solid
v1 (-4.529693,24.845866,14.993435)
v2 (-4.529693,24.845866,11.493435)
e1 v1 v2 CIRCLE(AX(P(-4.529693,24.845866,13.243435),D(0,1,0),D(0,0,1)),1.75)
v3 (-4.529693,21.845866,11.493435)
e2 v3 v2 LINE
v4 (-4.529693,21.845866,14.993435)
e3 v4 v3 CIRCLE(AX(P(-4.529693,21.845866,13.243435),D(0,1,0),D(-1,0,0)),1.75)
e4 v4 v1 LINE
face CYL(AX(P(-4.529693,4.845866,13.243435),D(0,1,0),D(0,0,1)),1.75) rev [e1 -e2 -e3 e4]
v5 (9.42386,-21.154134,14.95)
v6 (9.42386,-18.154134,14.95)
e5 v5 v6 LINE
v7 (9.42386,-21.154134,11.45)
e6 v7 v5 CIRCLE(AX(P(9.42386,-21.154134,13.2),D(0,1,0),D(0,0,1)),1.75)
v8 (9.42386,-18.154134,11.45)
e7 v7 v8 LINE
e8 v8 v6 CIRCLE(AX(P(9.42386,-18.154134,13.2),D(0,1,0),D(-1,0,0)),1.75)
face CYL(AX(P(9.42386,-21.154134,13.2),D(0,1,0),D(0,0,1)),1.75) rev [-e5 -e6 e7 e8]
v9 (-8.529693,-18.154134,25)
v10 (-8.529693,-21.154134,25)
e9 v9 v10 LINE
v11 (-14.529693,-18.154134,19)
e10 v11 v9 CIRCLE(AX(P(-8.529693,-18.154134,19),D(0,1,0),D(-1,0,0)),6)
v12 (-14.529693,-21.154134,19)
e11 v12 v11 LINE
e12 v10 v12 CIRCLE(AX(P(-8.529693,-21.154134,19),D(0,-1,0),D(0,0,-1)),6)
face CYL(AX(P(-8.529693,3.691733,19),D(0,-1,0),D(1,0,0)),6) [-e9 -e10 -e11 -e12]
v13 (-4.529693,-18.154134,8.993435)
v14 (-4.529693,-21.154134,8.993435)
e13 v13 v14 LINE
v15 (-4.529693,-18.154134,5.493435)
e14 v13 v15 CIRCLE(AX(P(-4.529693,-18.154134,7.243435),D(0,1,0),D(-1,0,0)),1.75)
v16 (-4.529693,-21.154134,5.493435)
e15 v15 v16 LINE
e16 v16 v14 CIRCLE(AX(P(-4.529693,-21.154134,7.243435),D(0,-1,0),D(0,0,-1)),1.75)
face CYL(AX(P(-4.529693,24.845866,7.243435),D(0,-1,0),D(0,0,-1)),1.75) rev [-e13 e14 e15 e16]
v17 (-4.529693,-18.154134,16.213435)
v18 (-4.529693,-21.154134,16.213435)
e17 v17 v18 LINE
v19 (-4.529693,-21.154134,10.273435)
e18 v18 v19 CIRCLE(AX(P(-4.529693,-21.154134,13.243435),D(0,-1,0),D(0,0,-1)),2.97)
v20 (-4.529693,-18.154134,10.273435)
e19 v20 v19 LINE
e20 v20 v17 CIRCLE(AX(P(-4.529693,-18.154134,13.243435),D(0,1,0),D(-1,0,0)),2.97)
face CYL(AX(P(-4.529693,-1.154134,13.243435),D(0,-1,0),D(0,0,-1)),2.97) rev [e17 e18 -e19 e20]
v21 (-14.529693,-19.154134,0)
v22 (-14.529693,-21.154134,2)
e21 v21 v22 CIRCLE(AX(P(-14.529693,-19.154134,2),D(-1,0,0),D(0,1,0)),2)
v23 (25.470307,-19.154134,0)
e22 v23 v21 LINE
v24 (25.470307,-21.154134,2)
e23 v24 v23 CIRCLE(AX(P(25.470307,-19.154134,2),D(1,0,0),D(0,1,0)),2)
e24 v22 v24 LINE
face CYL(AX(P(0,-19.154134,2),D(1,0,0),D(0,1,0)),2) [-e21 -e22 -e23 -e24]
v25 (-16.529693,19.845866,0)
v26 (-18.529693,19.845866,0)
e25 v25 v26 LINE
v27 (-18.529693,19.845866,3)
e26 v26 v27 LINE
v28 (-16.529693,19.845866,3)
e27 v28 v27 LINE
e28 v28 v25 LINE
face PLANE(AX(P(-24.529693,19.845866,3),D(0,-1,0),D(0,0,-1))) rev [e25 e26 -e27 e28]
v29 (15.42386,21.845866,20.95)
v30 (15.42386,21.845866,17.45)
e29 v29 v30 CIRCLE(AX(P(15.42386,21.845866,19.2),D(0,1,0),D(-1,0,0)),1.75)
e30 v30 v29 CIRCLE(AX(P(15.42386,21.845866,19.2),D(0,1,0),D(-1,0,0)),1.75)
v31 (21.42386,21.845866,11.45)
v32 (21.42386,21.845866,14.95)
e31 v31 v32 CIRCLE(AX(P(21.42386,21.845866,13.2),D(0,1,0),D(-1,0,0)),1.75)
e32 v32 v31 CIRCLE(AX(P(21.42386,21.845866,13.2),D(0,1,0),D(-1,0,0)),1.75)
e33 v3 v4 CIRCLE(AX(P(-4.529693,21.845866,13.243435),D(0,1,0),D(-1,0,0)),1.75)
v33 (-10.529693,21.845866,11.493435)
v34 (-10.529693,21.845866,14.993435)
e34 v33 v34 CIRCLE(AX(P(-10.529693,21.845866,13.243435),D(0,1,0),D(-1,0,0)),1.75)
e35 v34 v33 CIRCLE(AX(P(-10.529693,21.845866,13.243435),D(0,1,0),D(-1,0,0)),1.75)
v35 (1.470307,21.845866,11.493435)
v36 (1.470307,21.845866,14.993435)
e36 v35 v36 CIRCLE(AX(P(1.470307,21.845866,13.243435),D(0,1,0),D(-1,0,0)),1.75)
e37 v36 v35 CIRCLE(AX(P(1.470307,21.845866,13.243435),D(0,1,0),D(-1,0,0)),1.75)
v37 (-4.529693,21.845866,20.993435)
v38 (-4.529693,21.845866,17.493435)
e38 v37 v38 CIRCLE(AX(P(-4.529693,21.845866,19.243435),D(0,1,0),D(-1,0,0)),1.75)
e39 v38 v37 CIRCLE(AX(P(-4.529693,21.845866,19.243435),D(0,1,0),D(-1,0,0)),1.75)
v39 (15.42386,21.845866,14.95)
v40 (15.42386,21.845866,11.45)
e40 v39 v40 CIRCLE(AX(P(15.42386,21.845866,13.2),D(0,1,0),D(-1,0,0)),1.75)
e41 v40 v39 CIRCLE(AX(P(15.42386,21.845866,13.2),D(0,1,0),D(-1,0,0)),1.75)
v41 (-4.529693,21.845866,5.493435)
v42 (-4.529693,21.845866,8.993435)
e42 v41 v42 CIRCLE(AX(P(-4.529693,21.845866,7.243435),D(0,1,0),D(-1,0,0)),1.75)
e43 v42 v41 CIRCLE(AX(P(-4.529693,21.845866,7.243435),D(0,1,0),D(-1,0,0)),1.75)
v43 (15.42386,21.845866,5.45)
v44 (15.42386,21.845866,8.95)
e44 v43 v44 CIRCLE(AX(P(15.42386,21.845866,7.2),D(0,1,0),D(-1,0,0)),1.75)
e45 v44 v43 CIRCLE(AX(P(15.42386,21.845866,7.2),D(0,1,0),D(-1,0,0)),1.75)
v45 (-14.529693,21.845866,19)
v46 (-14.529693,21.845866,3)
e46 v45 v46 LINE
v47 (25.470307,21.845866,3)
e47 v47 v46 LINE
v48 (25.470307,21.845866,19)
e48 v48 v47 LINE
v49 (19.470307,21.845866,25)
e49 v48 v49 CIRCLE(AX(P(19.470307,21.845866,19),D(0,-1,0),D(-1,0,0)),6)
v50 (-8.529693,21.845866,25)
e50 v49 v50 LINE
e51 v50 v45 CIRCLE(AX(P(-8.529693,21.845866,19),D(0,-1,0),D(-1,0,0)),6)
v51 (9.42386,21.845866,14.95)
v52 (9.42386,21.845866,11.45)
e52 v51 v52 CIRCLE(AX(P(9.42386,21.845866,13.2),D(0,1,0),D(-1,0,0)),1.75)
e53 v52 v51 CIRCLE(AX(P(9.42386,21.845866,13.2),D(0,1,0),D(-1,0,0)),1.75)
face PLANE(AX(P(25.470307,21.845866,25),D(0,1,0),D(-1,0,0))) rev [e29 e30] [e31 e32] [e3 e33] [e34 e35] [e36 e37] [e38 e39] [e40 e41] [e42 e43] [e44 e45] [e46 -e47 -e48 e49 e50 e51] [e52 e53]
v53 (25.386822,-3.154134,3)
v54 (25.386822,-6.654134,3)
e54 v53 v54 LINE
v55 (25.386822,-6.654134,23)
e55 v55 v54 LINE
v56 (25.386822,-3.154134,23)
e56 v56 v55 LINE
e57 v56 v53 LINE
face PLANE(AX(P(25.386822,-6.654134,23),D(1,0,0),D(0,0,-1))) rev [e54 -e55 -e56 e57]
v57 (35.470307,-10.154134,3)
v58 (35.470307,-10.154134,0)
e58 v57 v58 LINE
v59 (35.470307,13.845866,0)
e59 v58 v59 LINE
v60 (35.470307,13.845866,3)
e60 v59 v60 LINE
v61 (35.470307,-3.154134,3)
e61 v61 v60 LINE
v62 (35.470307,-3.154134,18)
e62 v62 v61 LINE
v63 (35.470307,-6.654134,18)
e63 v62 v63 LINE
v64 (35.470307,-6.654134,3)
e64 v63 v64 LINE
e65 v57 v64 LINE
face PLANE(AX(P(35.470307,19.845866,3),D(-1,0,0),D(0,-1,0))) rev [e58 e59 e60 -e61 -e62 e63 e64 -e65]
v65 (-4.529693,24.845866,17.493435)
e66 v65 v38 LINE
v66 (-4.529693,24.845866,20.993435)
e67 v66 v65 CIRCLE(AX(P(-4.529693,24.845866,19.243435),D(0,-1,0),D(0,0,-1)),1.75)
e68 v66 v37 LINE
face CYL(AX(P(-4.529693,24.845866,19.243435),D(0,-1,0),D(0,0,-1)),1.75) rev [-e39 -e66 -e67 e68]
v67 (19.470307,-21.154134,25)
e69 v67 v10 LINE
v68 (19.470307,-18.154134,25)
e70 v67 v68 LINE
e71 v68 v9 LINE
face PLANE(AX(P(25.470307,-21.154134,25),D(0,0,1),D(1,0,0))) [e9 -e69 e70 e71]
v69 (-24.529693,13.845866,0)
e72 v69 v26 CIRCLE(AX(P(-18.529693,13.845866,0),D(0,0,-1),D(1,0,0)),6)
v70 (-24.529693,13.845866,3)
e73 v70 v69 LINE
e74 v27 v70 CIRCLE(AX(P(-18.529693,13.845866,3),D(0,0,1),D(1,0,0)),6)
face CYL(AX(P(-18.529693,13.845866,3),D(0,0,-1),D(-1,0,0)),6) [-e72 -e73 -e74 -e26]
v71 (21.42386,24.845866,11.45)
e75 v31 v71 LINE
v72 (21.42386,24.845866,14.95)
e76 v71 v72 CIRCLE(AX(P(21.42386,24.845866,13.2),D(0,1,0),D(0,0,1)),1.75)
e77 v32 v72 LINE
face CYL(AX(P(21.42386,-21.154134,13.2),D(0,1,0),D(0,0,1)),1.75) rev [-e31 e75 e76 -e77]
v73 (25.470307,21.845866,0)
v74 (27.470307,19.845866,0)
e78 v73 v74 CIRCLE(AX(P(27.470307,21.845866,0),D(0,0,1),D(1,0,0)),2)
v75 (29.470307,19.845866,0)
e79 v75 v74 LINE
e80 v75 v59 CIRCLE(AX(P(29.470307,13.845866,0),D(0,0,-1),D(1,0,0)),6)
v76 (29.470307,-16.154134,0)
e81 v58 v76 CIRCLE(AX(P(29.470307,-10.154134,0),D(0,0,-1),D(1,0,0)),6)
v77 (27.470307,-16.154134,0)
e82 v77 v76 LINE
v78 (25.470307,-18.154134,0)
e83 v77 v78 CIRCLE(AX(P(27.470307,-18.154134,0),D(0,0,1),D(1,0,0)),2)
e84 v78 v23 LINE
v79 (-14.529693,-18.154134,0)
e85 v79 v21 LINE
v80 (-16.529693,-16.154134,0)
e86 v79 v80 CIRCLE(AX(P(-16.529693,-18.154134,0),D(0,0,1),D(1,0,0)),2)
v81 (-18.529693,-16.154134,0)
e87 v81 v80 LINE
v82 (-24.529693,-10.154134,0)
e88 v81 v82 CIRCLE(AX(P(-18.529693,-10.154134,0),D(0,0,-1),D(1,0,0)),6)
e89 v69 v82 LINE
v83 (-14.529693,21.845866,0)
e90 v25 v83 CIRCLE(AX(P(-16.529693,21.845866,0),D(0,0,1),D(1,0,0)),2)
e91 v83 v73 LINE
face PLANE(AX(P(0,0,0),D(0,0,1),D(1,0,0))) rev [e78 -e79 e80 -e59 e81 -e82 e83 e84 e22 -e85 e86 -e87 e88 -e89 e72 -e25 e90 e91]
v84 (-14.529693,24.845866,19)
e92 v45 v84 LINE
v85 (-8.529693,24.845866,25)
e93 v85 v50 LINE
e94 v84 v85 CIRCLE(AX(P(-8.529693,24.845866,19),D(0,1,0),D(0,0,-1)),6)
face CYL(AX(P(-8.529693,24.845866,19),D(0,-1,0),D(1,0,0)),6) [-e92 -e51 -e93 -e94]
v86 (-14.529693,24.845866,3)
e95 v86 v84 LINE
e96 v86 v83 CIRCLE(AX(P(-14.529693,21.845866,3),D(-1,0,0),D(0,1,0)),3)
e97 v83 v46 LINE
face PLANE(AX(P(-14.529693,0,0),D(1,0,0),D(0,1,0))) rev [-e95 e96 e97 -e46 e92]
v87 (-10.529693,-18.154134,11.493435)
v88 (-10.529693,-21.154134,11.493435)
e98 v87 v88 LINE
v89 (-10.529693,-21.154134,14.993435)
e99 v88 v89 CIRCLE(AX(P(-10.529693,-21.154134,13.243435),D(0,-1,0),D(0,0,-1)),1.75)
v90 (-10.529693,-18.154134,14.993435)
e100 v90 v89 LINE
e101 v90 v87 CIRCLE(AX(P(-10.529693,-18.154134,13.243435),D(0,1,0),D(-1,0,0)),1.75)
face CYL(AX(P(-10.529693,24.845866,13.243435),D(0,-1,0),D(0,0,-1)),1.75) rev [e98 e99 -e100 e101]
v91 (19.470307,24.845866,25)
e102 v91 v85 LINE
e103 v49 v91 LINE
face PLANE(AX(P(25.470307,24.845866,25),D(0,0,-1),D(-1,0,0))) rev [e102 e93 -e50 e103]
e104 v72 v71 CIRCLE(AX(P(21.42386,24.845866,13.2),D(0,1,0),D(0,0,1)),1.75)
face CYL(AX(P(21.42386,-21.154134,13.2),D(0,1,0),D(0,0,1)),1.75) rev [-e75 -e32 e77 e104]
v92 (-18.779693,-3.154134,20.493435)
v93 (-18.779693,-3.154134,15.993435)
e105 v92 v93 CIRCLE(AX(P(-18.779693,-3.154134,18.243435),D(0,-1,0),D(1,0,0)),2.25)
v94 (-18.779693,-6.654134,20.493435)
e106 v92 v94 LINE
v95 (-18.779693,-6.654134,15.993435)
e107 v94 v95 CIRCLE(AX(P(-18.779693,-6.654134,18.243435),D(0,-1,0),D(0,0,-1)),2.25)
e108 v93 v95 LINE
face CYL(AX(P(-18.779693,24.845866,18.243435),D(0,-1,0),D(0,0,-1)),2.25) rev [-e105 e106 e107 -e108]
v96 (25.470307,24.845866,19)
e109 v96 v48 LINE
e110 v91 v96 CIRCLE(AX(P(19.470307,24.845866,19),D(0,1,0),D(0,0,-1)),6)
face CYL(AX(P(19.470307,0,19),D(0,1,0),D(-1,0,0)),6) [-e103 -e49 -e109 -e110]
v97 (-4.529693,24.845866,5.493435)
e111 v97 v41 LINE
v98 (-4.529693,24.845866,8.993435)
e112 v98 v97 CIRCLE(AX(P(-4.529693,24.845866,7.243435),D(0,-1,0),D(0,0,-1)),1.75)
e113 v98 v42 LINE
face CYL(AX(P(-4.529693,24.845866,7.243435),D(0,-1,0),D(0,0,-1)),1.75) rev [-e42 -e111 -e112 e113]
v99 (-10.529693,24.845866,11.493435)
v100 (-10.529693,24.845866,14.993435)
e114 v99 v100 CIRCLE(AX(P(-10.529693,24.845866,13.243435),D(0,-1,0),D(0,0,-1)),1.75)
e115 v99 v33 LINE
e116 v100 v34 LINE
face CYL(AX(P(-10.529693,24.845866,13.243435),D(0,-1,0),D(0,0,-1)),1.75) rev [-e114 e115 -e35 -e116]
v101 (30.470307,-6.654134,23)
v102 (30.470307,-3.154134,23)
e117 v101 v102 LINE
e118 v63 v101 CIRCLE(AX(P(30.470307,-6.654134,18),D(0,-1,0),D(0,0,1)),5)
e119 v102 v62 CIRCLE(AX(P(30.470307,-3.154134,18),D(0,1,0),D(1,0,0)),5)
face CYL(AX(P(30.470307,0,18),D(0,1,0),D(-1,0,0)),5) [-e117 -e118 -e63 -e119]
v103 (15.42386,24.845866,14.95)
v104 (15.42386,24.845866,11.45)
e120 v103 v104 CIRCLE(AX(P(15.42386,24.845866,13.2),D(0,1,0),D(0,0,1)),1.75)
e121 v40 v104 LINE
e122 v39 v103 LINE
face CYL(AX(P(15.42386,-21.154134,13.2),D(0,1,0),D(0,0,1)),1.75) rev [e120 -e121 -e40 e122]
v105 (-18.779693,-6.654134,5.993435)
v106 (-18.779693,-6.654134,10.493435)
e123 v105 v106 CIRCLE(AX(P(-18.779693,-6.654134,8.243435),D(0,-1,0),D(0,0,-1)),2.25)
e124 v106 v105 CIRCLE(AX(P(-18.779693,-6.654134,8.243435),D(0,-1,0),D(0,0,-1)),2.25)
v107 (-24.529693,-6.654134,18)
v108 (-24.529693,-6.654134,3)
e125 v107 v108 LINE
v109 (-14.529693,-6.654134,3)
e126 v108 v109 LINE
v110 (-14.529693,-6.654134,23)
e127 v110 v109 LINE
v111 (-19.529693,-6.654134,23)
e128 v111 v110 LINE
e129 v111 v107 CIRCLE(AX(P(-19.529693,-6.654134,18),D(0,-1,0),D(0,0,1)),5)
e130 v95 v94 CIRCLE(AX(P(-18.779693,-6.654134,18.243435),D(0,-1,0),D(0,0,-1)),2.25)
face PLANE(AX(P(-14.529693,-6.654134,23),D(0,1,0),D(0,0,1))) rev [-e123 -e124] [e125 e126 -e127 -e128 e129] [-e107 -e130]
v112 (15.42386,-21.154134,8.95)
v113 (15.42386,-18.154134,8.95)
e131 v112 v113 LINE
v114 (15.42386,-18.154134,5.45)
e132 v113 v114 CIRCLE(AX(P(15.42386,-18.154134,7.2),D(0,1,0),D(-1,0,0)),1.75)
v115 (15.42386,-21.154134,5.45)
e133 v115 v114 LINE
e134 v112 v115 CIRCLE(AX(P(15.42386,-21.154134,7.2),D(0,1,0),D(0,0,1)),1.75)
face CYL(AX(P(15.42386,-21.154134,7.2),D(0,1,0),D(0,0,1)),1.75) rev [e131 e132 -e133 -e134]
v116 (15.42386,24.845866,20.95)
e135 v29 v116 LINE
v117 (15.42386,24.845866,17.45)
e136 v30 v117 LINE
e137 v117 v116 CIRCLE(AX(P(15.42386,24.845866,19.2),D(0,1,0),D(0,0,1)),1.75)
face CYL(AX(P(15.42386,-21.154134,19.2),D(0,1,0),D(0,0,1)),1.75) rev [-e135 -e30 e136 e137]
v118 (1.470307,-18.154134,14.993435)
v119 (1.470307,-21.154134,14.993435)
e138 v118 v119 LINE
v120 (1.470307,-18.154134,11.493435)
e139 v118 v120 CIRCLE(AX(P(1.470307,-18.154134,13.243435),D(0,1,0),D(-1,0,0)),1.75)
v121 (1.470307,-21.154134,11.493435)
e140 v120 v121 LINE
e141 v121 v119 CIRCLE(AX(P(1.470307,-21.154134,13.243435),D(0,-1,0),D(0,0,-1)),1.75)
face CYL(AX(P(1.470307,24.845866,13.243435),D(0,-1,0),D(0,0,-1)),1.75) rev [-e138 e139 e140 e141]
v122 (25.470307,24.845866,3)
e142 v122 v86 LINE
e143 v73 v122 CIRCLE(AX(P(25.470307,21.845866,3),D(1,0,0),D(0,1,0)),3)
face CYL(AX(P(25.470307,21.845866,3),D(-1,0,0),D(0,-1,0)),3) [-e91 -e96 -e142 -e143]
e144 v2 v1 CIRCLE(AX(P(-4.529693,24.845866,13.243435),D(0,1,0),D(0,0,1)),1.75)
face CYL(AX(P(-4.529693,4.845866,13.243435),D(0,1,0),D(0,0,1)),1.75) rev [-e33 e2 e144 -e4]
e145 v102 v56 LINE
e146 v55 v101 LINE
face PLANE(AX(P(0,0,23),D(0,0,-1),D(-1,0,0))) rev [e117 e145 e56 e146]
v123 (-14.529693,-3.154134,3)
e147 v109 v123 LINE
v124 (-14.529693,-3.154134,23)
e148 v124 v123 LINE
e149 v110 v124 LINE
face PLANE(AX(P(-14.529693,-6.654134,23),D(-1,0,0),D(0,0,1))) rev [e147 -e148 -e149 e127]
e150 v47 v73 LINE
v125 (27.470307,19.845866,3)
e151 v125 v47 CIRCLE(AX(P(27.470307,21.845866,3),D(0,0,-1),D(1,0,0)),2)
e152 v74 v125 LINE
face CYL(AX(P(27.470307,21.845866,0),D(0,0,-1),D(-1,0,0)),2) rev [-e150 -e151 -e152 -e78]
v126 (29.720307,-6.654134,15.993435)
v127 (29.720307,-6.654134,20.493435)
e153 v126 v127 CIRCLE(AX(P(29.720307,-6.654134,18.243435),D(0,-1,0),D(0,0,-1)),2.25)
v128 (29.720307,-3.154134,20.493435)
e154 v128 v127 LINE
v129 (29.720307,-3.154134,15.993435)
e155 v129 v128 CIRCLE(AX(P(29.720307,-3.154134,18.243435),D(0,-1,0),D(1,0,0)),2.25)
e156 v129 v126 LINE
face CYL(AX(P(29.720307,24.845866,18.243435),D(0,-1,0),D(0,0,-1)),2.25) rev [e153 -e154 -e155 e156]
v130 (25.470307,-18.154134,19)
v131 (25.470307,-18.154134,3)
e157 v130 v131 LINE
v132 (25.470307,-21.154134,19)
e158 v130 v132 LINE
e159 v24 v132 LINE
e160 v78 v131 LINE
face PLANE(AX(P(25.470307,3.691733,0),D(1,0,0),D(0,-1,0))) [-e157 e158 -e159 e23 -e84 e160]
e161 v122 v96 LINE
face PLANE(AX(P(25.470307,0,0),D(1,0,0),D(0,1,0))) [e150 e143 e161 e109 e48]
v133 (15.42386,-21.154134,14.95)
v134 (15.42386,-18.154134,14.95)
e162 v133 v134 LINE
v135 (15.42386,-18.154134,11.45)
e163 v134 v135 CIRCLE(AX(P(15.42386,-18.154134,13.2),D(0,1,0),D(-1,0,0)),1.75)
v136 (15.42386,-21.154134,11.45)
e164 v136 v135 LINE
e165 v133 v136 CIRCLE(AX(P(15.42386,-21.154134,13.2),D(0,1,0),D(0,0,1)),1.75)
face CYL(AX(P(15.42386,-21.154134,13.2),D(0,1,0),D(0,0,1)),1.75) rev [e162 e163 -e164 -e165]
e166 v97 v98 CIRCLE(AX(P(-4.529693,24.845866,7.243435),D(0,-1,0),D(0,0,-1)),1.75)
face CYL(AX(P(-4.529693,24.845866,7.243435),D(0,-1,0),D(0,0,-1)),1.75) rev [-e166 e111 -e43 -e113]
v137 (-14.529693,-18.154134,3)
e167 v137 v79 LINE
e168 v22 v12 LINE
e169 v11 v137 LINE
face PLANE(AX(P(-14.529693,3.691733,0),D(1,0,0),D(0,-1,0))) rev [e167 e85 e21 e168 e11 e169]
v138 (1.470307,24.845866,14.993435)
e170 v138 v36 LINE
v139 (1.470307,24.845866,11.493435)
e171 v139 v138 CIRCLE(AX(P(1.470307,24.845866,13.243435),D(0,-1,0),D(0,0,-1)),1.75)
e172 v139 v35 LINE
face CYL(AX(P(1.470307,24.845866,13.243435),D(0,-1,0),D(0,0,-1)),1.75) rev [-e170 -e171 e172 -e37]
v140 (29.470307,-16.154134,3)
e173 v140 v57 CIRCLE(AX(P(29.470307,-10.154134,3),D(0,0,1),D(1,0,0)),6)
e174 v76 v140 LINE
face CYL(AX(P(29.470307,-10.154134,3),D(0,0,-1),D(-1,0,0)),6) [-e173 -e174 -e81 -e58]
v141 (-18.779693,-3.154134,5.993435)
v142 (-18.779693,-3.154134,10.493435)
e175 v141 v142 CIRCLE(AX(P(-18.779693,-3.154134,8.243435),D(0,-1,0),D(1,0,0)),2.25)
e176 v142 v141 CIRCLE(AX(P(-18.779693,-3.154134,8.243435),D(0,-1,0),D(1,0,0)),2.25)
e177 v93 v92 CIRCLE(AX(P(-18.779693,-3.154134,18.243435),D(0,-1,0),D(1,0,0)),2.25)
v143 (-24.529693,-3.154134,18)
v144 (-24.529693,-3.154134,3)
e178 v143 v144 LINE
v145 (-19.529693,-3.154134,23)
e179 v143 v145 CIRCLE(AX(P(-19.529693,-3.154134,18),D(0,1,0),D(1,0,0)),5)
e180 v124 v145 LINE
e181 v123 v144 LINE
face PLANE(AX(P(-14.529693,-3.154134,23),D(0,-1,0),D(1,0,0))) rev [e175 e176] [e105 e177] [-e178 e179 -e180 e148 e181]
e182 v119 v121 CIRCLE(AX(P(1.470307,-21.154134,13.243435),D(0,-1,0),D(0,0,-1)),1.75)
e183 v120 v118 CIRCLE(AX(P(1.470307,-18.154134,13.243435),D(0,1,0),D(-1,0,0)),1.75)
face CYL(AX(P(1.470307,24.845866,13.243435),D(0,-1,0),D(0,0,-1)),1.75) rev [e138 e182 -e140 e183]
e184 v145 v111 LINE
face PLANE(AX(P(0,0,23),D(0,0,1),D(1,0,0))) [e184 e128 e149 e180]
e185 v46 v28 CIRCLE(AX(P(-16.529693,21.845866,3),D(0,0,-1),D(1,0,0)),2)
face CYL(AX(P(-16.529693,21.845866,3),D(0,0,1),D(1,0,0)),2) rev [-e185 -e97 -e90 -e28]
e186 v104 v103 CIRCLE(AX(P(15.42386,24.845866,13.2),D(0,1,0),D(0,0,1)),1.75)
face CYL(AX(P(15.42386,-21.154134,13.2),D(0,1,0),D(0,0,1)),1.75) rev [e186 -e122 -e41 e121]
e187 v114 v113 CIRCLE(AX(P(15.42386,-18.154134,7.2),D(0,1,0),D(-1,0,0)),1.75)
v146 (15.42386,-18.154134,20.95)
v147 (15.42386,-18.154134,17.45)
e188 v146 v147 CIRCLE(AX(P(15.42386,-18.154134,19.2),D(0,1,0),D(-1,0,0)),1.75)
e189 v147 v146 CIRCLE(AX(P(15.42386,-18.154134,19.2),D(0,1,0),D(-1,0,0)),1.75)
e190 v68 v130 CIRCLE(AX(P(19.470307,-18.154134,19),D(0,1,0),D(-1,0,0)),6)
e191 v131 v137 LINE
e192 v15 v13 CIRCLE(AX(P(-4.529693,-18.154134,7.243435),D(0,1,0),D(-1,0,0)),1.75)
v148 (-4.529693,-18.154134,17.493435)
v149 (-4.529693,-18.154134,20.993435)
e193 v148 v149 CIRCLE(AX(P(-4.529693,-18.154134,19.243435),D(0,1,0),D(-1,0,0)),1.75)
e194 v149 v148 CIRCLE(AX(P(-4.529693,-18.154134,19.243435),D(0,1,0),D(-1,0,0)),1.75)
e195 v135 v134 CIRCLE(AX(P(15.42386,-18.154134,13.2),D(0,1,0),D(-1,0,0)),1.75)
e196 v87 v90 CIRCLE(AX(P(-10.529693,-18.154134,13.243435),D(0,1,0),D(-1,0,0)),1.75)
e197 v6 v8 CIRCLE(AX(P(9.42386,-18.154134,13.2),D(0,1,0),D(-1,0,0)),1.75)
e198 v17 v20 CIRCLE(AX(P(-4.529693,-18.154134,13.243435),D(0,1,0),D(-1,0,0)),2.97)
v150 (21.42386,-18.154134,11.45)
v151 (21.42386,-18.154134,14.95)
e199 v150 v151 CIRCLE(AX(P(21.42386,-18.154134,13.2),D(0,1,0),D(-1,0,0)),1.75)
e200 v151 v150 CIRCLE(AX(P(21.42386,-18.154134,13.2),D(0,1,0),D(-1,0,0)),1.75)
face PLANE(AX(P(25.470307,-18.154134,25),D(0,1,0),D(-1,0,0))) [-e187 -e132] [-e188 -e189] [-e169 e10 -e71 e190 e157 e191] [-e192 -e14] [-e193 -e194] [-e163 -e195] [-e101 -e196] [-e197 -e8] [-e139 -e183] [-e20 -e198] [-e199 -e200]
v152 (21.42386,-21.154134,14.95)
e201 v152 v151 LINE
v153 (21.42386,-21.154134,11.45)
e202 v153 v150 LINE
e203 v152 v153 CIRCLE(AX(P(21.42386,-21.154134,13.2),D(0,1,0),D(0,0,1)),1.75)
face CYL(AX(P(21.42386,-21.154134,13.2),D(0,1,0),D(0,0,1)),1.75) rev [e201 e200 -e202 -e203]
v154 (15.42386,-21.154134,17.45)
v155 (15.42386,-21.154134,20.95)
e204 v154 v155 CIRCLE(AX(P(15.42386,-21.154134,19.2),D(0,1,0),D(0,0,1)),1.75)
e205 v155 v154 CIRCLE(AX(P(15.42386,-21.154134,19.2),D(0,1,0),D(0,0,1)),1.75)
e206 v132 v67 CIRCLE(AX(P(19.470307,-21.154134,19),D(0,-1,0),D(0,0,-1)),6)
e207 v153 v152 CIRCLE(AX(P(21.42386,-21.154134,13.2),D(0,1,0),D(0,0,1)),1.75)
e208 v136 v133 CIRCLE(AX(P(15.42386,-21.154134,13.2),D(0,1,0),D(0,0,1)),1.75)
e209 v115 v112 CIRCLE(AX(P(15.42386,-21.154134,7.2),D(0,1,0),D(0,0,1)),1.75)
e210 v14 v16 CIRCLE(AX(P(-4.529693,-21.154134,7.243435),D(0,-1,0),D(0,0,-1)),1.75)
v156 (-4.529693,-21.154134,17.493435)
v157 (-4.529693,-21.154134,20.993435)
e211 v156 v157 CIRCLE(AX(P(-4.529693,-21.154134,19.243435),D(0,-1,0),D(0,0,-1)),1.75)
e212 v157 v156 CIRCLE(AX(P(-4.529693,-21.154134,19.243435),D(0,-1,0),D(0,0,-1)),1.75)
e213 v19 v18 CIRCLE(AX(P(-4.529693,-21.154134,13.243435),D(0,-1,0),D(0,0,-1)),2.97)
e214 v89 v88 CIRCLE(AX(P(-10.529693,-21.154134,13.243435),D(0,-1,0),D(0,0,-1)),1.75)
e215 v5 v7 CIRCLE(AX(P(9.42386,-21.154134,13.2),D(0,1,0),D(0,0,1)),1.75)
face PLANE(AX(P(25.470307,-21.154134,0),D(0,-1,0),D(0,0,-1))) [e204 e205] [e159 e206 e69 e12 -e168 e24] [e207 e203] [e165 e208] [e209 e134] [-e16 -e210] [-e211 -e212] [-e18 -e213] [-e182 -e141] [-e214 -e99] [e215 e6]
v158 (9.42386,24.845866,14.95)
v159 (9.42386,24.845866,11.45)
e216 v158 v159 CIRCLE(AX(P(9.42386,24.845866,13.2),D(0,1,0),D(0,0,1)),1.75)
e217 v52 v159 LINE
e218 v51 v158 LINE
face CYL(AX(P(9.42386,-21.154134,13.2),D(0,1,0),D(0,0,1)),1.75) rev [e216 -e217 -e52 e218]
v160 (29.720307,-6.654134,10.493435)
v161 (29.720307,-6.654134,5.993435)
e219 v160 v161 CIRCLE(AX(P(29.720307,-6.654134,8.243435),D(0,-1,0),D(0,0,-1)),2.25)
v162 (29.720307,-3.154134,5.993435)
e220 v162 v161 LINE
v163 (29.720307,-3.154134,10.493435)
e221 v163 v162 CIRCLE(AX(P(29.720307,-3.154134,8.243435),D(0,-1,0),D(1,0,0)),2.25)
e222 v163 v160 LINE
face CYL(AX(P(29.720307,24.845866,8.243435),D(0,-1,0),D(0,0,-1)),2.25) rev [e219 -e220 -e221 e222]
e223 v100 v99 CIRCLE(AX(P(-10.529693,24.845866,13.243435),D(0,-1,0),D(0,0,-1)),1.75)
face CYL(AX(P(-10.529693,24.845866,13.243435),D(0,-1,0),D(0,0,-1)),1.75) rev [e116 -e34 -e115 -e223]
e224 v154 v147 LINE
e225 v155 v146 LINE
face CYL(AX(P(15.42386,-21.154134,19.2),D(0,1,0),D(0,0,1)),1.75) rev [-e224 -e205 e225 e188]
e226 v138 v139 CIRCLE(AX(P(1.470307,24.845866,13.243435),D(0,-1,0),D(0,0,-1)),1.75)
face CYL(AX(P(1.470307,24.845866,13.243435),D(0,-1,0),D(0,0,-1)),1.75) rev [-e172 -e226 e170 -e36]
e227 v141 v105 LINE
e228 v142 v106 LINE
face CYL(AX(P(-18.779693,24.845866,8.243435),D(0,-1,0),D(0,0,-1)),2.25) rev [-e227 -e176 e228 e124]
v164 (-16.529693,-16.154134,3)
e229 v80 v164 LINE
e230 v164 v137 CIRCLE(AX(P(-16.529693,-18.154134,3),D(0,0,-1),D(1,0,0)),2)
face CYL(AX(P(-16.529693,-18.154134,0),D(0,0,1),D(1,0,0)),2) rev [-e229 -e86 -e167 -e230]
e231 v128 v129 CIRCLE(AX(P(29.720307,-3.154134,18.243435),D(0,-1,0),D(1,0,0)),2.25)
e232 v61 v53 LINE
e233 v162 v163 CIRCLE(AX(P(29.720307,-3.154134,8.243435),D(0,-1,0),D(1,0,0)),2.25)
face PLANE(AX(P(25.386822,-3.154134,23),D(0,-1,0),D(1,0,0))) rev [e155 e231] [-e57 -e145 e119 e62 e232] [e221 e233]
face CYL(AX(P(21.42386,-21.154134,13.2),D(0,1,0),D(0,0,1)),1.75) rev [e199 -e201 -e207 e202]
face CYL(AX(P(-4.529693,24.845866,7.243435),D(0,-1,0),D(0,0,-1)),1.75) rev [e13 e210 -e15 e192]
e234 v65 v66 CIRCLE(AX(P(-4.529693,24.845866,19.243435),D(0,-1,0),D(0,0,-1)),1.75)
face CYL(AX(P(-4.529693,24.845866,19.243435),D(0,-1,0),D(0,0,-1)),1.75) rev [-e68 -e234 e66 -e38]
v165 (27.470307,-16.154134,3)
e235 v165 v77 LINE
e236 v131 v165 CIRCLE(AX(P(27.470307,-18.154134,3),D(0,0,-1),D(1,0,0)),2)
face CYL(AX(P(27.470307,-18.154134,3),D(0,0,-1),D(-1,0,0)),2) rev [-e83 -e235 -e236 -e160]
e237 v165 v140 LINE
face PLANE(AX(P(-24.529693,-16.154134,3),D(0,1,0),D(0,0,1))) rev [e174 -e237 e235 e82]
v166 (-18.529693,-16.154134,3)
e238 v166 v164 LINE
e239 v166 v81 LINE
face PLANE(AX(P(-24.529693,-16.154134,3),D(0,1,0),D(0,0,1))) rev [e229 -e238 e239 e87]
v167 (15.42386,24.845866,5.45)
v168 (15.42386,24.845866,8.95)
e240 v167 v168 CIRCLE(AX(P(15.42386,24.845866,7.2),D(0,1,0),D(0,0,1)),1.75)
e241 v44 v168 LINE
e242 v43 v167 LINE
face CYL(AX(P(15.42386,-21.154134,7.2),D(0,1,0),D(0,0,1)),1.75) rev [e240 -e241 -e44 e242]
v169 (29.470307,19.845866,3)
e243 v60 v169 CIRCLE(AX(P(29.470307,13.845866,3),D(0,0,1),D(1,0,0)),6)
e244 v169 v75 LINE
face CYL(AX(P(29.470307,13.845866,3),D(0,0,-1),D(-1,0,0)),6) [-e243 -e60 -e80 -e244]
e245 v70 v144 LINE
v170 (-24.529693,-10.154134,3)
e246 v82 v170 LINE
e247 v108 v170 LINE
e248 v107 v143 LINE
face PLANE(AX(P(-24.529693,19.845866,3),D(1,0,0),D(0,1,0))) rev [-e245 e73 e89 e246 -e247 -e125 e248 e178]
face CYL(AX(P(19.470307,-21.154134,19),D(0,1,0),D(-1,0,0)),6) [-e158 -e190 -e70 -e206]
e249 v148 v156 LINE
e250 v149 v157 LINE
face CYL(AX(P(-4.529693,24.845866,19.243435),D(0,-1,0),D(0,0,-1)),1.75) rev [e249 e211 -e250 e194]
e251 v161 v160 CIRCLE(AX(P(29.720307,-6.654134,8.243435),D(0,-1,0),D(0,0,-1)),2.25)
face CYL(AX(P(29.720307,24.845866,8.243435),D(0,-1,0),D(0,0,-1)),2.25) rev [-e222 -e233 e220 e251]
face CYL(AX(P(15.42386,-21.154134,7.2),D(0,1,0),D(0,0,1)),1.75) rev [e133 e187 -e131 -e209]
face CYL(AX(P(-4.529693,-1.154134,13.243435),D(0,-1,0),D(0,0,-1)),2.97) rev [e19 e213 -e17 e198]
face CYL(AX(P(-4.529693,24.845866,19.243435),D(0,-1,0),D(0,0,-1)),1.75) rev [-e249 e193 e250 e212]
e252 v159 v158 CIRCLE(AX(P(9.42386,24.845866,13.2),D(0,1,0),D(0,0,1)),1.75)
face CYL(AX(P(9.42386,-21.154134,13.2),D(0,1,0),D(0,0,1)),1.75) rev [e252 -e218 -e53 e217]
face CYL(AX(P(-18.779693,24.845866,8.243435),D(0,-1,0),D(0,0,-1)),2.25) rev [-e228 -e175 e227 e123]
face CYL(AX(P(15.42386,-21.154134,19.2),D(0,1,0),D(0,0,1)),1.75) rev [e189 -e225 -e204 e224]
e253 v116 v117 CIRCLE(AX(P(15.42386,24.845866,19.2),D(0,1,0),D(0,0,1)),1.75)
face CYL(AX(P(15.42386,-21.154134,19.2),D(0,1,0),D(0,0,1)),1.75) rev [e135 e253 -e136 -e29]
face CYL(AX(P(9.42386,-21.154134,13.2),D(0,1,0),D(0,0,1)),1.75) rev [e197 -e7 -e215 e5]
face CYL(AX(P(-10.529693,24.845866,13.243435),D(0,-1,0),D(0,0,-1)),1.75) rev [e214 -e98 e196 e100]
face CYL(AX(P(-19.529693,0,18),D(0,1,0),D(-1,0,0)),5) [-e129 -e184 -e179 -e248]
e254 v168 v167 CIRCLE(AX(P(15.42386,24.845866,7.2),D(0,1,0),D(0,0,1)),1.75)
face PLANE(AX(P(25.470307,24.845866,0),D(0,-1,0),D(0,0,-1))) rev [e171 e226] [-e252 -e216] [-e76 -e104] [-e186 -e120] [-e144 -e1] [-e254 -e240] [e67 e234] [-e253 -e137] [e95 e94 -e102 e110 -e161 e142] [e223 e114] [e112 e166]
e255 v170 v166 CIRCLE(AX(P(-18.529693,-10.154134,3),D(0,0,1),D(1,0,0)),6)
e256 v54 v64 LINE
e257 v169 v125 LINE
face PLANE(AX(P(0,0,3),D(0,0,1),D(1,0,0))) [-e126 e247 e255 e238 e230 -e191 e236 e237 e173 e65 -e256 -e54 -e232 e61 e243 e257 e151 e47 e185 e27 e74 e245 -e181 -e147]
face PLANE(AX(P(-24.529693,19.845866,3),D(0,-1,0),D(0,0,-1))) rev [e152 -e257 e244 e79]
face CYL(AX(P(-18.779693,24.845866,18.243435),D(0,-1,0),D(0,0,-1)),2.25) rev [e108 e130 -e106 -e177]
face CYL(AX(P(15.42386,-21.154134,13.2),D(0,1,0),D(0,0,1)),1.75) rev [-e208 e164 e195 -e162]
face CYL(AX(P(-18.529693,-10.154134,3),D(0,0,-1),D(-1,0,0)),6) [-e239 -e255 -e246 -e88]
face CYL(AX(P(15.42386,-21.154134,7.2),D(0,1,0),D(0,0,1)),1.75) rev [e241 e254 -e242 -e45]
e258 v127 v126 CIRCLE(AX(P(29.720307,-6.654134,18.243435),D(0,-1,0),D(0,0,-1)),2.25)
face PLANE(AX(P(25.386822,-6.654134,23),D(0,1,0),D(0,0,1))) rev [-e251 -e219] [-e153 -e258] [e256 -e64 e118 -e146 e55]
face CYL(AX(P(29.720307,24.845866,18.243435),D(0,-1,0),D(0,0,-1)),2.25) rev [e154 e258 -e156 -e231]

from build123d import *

# Parameters (mm, degrees)
SKETCH1_W           = 60
SKETCH1_H           = 36
BOSS_EXTRUDE1_DEPTH = 3
BOSS_EXTRUDE2_DEPTH = 20
FILLET2_R           = 3
FILLET3_R           = 2
FILLET4_R           = 2
FILLET5_R           = 2
FILLET6_R           = 6
FILLET7_R           = 6
SKETCH4_R           = 1.75
CUT_EXTRUDE1_DEPTH  = 64.238774978
SKETCH6_W           = 10.083484861
SKETCH6_H           = 3.5
SKETCH6_W_2         = 10
BOSS_EXTRUDE3_DEPTH = 20
FILLET8_R           = 5
SKETCH7_R           = 2.25
CUT_EXTRUDE2_DEPTH  = 54.622687928
SKETCH8_R           = 2.97
CUT_EXTRUDE3_DEPTH  = 20
SKETCH9_R           = 1.75
CUT_EXTRUDE4_DEPTH  = 64.238774978
SKETCH10_R          = 1.75
CUT_EXTRUDE5_DEPTH  = 20


with BuildPart() as part:
    # Sketch1 → Boss-Extrude1 (new body)
    with BuildSketch(Plane.XY):
        with Locations((5.470306746, 1.845866319)):
            Rectangle(SKETCH1_W, SKETCH1_H)
    extrude(amount=BOSS_EXTRUDE1_DEPTH)

    # Sketch3 → Boss-Extrude2 (add, symmetric)
    with BuildSketch(Plane(origin=(5.470306746, 0, 0), x_dir=(0, 0, -1), z_dir=(1, 0, 0))):
        Polygon((0, 22.869721484), (0, 24.845866319), (-25, 24.845866319), (-25, 21.845866319), (-3, 21.845866319), (-3, 19.845866319), (0, 19.845866319), align=None)
    boss_extrude2 = extrude(amount=BOSS_EXTRUDE2_DEPTH, both=True)

    # Fillet2
    fillet2_edges = [part.edges().sort_by_distance(p)[0] for p in [
        (5.470306746, 24.845866319, 0),
    ]]
    fillet(fillet2_edges, radius=FILLET2_R)

    # Fillet3
    fillet3_edges = [part.edges().sort_by_distance(p)[0] for p in [
        (-14.529693254, 19.845866319, 1.5),
        (25.470306746, 19.845866319, 1.5),
    ]]
    fillet(fillet3_edges, radius=FILLET3_R)

    # Mirror2: Boss-Extrude2 across plane
    add(boss_extrude2.mirror(Plane(origin=(0, 1.845866319, 0), x_dir=(0, 0, 1), z_dir=(0, -1, 0))))

    # Fillet4
    fillet4_edges = [part.edges().sort_by_distance(p)[0] for p in [
        (25.470306746, -16.154133681, 1.5),
        (-14.529693254, -16.154133681, 1.5),
    ]]
    fillet(fillet4_edges, radius=FILLET4_R)

    # Fillet5
    fillet5_edges = [part.edges().sort_by_distance(p)[0] for p in [
        (5.470306746, -21.154133681, 0),
    ]]
    fillet(fillet5_edges, radius=FILLET5_R)

    # Fillet6
    fillet6_edges = [part.edges().sort_by_distance(p)[0] for p in [
        (-24.529693254, -16.154133681, 1.5),
        (-24.529693254, 19.845866319, 1.5),
        (35.470306746, -16.154133681, 1.5),
        (35.470306746, 19.845866319, 1.5),
    ]]
    fillet(fillet6_edges, radius=FILLET6_R)

    # Fillet7
    fillet7_edges = [part.edges().sort_by_distance(p)[0] for p in [
        (-14.529693254, 23.345866319, 25),
        (25.470306746, 23.345866319, 25),
        (25.470306746, -19.654133681, 25),
        (-14.529693254, -19.654133681, 25),
    ]]
    fillet(fillet7_edges, radius=FILLET7_R)

    # Sketch4 → Cut-Extrude1 (cut, through all)
    with BuildSketch(Plane(origin=(0, 24.845866319, 0), x_dir=(1, 0, 0), z_dir=(0, 1, 0))):
        with Locations(Location((15.423860137, -19.2, 0), (0, 0, 270))):
            Circle(SKETCH4_R)
        with Locations(Location((9.423860137, -13.2, 0), (0, 0, 270))):
            Circle(SKETCH4_R)
        with Locations(Location((15.423860137, -7.2, 0), (0, 0, 270))):
            Circle(SKETCH4_R)
        with Locations(Location((21.423860137, -13.2, 0), (0, 0, 270))):
            Circle(SKETCH4_R)
        with Locations(Location((15.423860137, -13.2, 0), (0, 0, 270))):
            Circle(SKETCH4_R)
    extrude(amount=-CUT_EXTRUDE1_DEPTH, mode=Mode.SUBTRACT)

    # Sketch6 → Boss-Extrude3 (add)
    with BuildSketch(Plane.XY.offset(3)):
        with Locations((30.428564316, -4.904133681)):
            Rectangle(SKETCH6_W, SKETCH6_H)
        with Locations((-19.529693254, -4.904133681)):
            Rectangle(SKETCH6_W_2, SKETCH6_H)
    extrude(amount=BOSS_EXTRUDE3_DEPTH)

    # Fillet8
    fillet8_edges = [part.edges().sort_by_distance(p)[0] for p in [
        (35.470306746, -4.904133681, 23),
        (-24.529693254, -4.904133681, 23),
    ]]
    fillet(fillet8_edges, radius=FILLET8_R)

    # Sketch7 → Cut-Extrude2 (cut, through all)
    with BuildSketch(Plane.XZ.offset(6.654133681)):
        with Locations(Location((29.720306746, 18.243434955, 0), (0, 0, 270))):
            Circle(SKETCH7_R)
        with Locations(Location((29.720306746, 8.243434955, 0), (0, 0, 270))):
            Circle(SKETCH7_R)
        with Locations(Location((-18.779693254, 18.243434955, 0), (0, 0, 270))):
            Circle(SKETCH7_R)
        with Locations(Location((-18.779693254, 8.243434955, 0), (0, 0, 270))):
            Circle(SKETCH7_R)
    extrude(amount=-CUT_EXTRUDE2_DEPTH, mode=Mode.SUBTRACT)

    # Sketch8 → Cut-Extrude3 (cut)
    with BuildSketch(Plane.XZ.offset(21.154133681)):
        with Locations(Location((-4.529693254, 13.243434955, 0), (0, 0, 270))):
            Circle(SKETCH8_R)
    extrude(amount=-CUT_EXTRUDE3_DEPTH, mode=Mode.SUBTRACT)

    # Sketch9 → Cut-Extrude4 (cut, through all)
    with BuildSketch(Plane.XZ.offset(21.154133681)):
        with Locations(Location((-4.529693254, 19.243434955, 0), (0, 0, 270))):
            Circle(SKETCH9_R)
        with Locations(Location((1.470306746, 13.243434955, 0), (0, 0, 270))):
            Circle(SKETCH9_R)
        with Locations(Location((-4.529693254, 7.243434955, 0), (0, 0, 270))):
            Circle(SKETCH9_R)
        with Locations(Location((-10.529693254, 13.243434955, 0), (0, 0, 270))):
            Circle(SKETCH9_R)
    extrude(amount=-CUT_EXTRUDE4_DEPTH, mode=Mode.SUBTRACT)

    # Sketch10 → Cut-Extrude5 (cut)
    with BuildSketch(Plane(origin=(0, 24.845866319, 0), x_dir=(1, 0, 0), z_dir=(0, 1, 0))):
        with Locations(Location((-4.529693254, -13.243434955, 0), (0, 0, 270))):
            Circle(SKETCH10_R)
    extrude(amount=-CUT_EXTRUDE5_DEPTH, mode=Mode.SUBTRACT)


solid = part.part
